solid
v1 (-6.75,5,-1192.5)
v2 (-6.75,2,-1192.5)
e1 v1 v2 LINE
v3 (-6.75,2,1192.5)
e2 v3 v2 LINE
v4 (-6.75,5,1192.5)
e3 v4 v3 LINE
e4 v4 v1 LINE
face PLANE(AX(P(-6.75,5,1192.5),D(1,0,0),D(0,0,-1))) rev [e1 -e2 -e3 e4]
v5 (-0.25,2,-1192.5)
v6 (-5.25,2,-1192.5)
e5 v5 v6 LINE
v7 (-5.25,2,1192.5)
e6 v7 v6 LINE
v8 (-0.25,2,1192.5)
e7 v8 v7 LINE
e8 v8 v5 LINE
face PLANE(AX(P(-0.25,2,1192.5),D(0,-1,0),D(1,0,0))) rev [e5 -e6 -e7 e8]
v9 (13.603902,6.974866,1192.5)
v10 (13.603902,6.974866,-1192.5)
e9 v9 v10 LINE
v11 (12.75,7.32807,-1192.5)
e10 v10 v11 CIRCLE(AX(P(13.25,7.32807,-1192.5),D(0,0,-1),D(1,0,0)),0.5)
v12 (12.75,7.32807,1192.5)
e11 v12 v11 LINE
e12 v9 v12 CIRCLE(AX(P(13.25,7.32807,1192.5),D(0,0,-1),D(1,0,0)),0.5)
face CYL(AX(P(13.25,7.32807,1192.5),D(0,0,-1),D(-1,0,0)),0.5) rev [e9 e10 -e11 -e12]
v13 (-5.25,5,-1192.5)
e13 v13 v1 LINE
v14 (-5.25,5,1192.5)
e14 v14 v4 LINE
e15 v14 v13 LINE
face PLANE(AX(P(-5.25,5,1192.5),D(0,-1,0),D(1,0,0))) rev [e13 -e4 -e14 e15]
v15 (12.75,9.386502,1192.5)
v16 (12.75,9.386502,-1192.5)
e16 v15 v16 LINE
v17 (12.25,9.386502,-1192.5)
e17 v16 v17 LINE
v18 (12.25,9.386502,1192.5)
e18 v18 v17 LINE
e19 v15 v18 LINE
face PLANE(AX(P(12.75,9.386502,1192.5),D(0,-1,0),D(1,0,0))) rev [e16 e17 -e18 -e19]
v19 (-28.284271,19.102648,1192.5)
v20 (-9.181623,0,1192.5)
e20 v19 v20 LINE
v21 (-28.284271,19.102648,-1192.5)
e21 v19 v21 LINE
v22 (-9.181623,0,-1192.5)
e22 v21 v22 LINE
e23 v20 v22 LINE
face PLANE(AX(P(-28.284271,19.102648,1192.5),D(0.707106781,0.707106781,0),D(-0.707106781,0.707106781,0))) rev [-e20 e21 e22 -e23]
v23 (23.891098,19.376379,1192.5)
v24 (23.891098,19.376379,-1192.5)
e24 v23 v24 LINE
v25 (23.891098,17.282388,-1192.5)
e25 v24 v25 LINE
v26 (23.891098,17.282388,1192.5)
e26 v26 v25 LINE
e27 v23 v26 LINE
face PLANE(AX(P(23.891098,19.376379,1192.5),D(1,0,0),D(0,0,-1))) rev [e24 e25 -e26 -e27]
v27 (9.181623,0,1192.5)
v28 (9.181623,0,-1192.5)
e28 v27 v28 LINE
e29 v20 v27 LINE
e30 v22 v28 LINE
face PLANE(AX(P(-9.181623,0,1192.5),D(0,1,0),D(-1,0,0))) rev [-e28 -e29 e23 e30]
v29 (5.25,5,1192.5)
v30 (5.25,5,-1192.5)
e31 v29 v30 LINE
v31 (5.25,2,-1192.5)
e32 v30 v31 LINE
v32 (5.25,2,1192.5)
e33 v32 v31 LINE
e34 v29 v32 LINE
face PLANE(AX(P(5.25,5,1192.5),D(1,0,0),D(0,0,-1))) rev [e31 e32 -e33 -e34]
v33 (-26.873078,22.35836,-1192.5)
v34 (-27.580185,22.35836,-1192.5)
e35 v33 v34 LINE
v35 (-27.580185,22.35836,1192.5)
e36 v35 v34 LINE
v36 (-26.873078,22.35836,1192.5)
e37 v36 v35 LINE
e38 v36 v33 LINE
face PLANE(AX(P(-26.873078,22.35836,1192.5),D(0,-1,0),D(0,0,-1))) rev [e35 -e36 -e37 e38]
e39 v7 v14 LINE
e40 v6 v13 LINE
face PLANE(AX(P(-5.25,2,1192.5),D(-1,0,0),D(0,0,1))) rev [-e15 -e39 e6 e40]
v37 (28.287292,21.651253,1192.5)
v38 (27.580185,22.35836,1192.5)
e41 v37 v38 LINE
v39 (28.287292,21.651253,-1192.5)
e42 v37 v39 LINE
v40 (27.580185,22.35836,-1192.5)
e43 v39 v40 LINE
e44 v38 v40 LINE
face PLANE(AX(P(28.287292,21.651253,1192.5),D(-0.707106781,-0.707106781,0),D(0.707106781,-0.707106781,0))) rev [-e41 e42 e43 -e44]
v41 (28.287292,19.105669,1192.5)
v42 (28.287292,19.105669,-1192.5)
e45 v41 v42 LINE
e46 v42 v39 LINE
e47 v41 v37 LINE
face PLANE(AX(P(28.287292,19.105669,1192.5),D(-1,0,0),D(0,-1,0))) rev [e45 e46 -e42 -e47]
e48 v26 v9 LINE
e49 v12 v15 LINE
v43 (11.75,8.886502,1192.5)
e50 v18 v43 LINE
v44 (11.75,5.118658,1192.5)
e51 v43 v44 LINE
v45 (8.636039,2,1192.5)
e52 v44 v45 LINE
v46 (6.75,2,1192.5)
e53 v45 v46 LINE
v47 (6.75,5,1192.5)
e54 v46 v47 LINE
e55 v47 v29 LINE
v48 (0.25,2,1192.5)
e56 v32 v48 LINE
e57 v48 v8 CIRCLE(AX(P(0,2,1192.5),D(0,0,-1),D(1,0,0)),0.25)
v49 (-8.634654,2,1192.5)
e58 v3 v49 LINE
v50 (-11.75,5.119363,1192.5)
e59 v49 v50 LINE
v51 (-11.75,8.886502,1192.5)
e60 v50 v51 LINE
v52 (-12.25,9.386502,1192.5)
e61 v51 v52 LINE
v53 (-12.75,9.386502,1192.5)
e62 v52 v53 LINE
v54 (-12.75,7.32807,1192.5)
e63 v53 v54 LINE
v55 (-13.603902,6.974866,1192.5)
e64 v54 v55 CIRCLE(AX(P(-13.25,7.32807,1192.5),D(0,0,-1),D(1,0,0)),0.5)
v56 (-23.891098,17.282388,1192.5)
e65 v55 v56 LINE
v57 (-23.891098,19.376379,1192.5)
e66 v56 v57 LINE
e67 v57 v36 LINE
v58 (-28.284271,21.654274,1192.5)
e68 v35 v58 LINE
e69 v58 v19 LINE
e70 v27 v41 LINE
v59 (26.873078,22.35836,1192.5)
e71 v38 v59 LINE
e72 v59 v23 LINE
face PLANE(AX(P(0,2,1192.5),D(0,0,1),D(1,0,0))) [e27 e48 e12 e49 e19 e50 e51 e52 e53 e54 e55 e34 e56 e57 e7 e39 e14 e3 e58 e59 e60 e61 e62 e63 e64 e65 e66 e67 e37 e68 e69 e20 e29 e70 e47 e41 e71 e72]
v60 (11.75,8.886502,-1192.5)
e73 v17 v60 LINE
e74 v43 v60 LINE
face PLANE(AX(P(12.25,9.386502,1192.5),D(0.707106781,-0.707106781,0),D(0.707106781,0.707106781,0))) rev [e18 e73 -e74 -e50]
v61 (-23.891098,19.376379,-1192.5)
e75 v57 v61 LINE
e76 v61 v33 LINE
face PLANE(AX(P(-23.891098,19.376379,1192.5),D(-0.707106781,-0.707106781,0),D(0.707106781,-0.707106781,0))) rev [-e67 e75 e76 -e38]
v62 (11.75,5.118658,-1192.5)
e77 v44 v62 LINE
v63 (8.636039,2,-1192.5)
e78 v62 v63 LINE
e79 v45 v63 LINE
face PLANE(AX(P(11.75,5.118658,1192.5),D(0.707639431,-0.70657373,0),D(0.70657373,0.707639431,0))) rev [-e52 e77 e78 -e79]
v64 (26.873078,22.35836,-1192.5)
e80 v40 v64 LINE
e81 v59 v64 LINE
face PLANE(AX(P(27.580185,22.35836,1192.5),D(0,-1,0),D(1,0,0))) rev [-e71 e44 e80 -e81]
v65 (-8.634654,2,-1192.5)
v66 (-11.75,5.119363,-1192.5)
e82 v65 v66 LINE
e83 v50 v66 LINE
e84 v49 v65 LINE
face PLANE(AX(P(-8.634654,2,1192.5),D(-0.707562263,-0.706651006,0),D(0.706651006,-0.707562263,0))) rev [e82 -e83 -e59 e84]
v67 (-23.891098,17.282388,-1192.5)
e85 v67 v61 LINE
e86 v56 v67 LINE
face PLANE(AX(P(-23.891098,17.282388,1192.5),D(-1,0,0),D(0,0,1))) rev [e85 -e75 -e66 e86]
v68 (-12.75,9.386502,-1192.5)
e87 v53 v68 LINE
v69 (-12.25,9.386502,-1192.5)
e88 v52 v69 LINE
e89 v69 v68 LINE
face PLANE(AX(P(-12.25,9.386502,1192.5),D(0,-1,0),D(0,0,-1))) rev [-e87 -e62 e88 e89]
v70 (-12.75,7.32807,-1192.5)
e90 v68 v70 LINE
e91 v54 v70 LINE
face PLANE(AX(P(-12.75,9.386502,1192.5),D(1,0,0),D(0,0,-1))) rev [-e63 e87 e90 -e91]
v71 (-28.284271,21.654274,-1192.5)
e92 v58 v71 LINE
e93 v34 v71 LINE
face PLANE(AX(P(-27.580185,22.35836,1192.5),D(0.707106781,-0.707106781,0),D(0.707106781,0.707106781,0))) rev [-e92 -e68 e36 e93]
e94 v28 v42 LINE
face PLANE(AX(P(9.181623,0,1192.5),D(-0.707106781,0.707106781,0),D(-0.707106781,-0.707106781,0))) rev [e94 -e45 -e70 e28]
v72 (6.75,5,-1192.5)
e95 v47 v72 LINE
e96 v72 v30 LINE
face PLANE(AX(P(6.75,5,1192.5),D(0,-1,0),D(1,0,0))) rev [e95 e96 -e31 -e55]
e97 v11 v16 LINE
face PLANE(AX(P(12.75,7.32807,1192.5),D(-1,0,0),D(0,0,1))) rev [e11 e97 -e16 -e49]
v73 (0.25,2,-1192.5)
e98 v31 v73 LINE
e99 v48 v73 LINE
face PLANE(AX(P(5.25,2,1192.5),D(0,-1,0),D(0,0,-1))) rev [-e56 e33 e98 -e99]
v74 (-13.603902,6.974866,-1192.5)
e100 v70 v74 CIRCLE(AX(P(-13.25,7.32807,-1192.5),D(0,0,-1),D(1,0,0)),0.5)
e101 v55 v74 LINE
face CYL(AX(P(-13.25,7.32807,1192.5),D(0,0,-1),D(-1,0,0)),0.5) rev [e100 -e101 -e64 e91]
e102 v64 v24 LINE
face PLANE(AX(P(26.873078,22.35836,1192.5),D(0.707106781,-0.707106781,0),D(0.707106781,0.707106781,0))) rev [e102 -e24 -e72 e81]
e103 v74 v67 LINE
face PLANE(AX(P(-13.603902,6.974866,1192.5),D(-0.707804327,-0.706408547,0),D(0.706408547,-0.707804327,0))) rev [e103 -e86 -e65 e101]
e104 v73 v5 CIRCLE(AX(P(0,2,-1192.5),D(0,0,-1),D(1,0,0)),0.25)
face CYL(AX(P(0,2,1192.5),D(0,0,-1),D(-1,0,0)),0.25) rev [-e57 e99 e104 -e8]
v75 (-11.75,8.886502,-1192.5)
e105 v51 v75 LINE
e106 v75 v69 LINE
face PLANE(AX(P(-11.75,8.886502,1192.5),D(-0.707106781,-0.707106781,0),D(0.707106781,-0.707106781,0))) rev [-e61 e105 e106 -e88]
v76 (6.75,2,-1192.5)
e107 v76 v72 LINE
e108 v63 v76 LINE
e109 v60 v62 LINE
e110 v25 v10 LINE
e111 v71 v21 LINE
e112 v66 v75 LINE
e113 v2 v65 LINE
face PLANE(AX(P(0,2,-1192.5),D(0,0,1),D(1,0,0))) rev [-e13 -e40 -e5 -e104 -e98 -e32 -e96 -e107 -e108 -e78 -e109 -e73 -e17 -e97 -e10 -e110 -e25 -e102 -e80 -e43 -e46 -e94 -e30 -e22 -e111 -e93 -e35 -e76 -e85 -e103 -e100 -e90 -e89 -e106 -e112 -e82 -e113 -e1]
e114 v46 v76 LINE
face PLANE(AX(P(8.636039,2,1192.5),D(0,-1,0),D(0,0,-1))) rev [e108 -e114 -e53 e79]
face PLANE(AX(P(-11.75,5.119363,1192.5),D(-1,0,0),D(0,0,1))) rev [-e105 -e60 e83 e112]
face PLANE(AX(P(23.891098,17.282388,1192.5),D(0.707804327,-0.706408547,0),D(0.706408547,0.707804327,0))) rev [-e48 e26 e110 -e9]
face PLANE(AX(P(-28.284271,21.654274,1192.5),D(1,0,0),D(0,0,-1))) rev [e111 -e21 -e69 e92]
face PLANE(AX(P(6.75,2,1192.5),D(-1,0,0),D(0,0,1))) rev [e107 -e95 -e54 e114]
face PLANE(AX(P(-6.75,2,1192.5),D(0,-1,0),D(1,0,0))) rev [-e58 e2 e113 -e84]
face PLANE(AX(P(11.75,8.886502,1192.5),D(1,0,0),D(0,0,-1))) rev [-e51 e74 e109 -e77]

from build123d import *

# Parameters (mm, degrees)
EXTRUDE_1_DEPTH = 1192.5


with BuildPart() as part:
    # 草图2 → 凸台-拉伸1 (new, symmetric)
    with BuildSketch(Plane.XY):
        with BuildLine():
            Line((6.75, 5), (5.25, 5))
            Line((5.25, 5), (5.25, 2))
            Line((5.25, 2), (0.25, 2))
            ThreePointArc((0.25, 2), (0, 1.75), (-0.25, 2))
            Line((-0.25, 2), (-5.25, 2))
            Line((-5.25, 2), (-5.25, 5))
            Line((-5.25, 5), (-6.75, 5))
            Line((-6.75, 5), (-6.75, 2))
            Line((-6.75, 2), (-8.634653896, 2))
            Line((-8.634653896, 2), (-11.75, 5.119363474))
            Line((-11.75, 5.119363474), (-11.75, 8.88650173))
            Line((-11.75, 8.88650173), (-12.25, 9.38650173))
            Line((-12.25, 9.38650173), (-12.75, 9.38650173))
            Line((-12.75, 9.38650173), (-12.75, 7.328070483))
            ThreePointArc((-12.75, 7.328070483), (-13.058886266, 6.866036349), (-13.603902163, 6.97486621))
            Line((-13.603902163, 6.97486621), (-23.891097866, 17.282388203))
            Line((-23.891097866, 17.282388203), (-23.891097866, 19.37637924))
            Line((-23.891097866, 19.37637924), (-26.873078382, 22.358359756))
            Line((-26.873078382, 22.358359756), (-27.580185163, 22.358359756))
            Line((-27.580185163, 22.358359756), (-28.284271248, 21.654273671))
            Line((-28.284271248, 21.654273671), (-28.284271248, 19.102647866))
            Line((-28.284271248, 19.102647866), (-9.181623382, 0))
            Line((-9.181623382, 0), (9.181623382, 0))
            Line((9.181623382, 0), (28.287291944, 19.105668562))
            Line((28.287291944, 19.105668562), (28.287291944, 21.651252975))
            Line((28.287291944, 21.651252975), (27.580185163, 22.358359756))
            Line((27.580185163, 22.358359756), (26.873078382, 22.358359756))
            Line((26.873078382, 22.358359756), (23.891097866, 19.376379241))
            Line((23.891097866, 19.376379241), (23.891097866, 17.282388203))
            Line((23.891097866, 17.282388203), (13.603902163, 6.97486621))
            ThreePointArc((13.603902163, 6.97486621), (13.058886266, 6.866036349), (12.75, 7.328070483))
            Line((12.75, 7.328070483), (12.75, 9.38650173))
            Line((12.75, 9.38650173), (12.25, 9.38650173))
            Line((12.25, 9.38650173), (11.75, 8.88650173))
            Line((11.75, 8.88650173), (11.75, 5.118657708))
            Line((11.75, 5.118657708), (8.636038969, 2))
            Line((8.636038969, 2), (6.75, 2))
            Line((6.75, 2), (6.75, 5))
        make_face()
    extrude(amount=EXTRUDE_1_DEPTH, both=True)


solid = part.part
